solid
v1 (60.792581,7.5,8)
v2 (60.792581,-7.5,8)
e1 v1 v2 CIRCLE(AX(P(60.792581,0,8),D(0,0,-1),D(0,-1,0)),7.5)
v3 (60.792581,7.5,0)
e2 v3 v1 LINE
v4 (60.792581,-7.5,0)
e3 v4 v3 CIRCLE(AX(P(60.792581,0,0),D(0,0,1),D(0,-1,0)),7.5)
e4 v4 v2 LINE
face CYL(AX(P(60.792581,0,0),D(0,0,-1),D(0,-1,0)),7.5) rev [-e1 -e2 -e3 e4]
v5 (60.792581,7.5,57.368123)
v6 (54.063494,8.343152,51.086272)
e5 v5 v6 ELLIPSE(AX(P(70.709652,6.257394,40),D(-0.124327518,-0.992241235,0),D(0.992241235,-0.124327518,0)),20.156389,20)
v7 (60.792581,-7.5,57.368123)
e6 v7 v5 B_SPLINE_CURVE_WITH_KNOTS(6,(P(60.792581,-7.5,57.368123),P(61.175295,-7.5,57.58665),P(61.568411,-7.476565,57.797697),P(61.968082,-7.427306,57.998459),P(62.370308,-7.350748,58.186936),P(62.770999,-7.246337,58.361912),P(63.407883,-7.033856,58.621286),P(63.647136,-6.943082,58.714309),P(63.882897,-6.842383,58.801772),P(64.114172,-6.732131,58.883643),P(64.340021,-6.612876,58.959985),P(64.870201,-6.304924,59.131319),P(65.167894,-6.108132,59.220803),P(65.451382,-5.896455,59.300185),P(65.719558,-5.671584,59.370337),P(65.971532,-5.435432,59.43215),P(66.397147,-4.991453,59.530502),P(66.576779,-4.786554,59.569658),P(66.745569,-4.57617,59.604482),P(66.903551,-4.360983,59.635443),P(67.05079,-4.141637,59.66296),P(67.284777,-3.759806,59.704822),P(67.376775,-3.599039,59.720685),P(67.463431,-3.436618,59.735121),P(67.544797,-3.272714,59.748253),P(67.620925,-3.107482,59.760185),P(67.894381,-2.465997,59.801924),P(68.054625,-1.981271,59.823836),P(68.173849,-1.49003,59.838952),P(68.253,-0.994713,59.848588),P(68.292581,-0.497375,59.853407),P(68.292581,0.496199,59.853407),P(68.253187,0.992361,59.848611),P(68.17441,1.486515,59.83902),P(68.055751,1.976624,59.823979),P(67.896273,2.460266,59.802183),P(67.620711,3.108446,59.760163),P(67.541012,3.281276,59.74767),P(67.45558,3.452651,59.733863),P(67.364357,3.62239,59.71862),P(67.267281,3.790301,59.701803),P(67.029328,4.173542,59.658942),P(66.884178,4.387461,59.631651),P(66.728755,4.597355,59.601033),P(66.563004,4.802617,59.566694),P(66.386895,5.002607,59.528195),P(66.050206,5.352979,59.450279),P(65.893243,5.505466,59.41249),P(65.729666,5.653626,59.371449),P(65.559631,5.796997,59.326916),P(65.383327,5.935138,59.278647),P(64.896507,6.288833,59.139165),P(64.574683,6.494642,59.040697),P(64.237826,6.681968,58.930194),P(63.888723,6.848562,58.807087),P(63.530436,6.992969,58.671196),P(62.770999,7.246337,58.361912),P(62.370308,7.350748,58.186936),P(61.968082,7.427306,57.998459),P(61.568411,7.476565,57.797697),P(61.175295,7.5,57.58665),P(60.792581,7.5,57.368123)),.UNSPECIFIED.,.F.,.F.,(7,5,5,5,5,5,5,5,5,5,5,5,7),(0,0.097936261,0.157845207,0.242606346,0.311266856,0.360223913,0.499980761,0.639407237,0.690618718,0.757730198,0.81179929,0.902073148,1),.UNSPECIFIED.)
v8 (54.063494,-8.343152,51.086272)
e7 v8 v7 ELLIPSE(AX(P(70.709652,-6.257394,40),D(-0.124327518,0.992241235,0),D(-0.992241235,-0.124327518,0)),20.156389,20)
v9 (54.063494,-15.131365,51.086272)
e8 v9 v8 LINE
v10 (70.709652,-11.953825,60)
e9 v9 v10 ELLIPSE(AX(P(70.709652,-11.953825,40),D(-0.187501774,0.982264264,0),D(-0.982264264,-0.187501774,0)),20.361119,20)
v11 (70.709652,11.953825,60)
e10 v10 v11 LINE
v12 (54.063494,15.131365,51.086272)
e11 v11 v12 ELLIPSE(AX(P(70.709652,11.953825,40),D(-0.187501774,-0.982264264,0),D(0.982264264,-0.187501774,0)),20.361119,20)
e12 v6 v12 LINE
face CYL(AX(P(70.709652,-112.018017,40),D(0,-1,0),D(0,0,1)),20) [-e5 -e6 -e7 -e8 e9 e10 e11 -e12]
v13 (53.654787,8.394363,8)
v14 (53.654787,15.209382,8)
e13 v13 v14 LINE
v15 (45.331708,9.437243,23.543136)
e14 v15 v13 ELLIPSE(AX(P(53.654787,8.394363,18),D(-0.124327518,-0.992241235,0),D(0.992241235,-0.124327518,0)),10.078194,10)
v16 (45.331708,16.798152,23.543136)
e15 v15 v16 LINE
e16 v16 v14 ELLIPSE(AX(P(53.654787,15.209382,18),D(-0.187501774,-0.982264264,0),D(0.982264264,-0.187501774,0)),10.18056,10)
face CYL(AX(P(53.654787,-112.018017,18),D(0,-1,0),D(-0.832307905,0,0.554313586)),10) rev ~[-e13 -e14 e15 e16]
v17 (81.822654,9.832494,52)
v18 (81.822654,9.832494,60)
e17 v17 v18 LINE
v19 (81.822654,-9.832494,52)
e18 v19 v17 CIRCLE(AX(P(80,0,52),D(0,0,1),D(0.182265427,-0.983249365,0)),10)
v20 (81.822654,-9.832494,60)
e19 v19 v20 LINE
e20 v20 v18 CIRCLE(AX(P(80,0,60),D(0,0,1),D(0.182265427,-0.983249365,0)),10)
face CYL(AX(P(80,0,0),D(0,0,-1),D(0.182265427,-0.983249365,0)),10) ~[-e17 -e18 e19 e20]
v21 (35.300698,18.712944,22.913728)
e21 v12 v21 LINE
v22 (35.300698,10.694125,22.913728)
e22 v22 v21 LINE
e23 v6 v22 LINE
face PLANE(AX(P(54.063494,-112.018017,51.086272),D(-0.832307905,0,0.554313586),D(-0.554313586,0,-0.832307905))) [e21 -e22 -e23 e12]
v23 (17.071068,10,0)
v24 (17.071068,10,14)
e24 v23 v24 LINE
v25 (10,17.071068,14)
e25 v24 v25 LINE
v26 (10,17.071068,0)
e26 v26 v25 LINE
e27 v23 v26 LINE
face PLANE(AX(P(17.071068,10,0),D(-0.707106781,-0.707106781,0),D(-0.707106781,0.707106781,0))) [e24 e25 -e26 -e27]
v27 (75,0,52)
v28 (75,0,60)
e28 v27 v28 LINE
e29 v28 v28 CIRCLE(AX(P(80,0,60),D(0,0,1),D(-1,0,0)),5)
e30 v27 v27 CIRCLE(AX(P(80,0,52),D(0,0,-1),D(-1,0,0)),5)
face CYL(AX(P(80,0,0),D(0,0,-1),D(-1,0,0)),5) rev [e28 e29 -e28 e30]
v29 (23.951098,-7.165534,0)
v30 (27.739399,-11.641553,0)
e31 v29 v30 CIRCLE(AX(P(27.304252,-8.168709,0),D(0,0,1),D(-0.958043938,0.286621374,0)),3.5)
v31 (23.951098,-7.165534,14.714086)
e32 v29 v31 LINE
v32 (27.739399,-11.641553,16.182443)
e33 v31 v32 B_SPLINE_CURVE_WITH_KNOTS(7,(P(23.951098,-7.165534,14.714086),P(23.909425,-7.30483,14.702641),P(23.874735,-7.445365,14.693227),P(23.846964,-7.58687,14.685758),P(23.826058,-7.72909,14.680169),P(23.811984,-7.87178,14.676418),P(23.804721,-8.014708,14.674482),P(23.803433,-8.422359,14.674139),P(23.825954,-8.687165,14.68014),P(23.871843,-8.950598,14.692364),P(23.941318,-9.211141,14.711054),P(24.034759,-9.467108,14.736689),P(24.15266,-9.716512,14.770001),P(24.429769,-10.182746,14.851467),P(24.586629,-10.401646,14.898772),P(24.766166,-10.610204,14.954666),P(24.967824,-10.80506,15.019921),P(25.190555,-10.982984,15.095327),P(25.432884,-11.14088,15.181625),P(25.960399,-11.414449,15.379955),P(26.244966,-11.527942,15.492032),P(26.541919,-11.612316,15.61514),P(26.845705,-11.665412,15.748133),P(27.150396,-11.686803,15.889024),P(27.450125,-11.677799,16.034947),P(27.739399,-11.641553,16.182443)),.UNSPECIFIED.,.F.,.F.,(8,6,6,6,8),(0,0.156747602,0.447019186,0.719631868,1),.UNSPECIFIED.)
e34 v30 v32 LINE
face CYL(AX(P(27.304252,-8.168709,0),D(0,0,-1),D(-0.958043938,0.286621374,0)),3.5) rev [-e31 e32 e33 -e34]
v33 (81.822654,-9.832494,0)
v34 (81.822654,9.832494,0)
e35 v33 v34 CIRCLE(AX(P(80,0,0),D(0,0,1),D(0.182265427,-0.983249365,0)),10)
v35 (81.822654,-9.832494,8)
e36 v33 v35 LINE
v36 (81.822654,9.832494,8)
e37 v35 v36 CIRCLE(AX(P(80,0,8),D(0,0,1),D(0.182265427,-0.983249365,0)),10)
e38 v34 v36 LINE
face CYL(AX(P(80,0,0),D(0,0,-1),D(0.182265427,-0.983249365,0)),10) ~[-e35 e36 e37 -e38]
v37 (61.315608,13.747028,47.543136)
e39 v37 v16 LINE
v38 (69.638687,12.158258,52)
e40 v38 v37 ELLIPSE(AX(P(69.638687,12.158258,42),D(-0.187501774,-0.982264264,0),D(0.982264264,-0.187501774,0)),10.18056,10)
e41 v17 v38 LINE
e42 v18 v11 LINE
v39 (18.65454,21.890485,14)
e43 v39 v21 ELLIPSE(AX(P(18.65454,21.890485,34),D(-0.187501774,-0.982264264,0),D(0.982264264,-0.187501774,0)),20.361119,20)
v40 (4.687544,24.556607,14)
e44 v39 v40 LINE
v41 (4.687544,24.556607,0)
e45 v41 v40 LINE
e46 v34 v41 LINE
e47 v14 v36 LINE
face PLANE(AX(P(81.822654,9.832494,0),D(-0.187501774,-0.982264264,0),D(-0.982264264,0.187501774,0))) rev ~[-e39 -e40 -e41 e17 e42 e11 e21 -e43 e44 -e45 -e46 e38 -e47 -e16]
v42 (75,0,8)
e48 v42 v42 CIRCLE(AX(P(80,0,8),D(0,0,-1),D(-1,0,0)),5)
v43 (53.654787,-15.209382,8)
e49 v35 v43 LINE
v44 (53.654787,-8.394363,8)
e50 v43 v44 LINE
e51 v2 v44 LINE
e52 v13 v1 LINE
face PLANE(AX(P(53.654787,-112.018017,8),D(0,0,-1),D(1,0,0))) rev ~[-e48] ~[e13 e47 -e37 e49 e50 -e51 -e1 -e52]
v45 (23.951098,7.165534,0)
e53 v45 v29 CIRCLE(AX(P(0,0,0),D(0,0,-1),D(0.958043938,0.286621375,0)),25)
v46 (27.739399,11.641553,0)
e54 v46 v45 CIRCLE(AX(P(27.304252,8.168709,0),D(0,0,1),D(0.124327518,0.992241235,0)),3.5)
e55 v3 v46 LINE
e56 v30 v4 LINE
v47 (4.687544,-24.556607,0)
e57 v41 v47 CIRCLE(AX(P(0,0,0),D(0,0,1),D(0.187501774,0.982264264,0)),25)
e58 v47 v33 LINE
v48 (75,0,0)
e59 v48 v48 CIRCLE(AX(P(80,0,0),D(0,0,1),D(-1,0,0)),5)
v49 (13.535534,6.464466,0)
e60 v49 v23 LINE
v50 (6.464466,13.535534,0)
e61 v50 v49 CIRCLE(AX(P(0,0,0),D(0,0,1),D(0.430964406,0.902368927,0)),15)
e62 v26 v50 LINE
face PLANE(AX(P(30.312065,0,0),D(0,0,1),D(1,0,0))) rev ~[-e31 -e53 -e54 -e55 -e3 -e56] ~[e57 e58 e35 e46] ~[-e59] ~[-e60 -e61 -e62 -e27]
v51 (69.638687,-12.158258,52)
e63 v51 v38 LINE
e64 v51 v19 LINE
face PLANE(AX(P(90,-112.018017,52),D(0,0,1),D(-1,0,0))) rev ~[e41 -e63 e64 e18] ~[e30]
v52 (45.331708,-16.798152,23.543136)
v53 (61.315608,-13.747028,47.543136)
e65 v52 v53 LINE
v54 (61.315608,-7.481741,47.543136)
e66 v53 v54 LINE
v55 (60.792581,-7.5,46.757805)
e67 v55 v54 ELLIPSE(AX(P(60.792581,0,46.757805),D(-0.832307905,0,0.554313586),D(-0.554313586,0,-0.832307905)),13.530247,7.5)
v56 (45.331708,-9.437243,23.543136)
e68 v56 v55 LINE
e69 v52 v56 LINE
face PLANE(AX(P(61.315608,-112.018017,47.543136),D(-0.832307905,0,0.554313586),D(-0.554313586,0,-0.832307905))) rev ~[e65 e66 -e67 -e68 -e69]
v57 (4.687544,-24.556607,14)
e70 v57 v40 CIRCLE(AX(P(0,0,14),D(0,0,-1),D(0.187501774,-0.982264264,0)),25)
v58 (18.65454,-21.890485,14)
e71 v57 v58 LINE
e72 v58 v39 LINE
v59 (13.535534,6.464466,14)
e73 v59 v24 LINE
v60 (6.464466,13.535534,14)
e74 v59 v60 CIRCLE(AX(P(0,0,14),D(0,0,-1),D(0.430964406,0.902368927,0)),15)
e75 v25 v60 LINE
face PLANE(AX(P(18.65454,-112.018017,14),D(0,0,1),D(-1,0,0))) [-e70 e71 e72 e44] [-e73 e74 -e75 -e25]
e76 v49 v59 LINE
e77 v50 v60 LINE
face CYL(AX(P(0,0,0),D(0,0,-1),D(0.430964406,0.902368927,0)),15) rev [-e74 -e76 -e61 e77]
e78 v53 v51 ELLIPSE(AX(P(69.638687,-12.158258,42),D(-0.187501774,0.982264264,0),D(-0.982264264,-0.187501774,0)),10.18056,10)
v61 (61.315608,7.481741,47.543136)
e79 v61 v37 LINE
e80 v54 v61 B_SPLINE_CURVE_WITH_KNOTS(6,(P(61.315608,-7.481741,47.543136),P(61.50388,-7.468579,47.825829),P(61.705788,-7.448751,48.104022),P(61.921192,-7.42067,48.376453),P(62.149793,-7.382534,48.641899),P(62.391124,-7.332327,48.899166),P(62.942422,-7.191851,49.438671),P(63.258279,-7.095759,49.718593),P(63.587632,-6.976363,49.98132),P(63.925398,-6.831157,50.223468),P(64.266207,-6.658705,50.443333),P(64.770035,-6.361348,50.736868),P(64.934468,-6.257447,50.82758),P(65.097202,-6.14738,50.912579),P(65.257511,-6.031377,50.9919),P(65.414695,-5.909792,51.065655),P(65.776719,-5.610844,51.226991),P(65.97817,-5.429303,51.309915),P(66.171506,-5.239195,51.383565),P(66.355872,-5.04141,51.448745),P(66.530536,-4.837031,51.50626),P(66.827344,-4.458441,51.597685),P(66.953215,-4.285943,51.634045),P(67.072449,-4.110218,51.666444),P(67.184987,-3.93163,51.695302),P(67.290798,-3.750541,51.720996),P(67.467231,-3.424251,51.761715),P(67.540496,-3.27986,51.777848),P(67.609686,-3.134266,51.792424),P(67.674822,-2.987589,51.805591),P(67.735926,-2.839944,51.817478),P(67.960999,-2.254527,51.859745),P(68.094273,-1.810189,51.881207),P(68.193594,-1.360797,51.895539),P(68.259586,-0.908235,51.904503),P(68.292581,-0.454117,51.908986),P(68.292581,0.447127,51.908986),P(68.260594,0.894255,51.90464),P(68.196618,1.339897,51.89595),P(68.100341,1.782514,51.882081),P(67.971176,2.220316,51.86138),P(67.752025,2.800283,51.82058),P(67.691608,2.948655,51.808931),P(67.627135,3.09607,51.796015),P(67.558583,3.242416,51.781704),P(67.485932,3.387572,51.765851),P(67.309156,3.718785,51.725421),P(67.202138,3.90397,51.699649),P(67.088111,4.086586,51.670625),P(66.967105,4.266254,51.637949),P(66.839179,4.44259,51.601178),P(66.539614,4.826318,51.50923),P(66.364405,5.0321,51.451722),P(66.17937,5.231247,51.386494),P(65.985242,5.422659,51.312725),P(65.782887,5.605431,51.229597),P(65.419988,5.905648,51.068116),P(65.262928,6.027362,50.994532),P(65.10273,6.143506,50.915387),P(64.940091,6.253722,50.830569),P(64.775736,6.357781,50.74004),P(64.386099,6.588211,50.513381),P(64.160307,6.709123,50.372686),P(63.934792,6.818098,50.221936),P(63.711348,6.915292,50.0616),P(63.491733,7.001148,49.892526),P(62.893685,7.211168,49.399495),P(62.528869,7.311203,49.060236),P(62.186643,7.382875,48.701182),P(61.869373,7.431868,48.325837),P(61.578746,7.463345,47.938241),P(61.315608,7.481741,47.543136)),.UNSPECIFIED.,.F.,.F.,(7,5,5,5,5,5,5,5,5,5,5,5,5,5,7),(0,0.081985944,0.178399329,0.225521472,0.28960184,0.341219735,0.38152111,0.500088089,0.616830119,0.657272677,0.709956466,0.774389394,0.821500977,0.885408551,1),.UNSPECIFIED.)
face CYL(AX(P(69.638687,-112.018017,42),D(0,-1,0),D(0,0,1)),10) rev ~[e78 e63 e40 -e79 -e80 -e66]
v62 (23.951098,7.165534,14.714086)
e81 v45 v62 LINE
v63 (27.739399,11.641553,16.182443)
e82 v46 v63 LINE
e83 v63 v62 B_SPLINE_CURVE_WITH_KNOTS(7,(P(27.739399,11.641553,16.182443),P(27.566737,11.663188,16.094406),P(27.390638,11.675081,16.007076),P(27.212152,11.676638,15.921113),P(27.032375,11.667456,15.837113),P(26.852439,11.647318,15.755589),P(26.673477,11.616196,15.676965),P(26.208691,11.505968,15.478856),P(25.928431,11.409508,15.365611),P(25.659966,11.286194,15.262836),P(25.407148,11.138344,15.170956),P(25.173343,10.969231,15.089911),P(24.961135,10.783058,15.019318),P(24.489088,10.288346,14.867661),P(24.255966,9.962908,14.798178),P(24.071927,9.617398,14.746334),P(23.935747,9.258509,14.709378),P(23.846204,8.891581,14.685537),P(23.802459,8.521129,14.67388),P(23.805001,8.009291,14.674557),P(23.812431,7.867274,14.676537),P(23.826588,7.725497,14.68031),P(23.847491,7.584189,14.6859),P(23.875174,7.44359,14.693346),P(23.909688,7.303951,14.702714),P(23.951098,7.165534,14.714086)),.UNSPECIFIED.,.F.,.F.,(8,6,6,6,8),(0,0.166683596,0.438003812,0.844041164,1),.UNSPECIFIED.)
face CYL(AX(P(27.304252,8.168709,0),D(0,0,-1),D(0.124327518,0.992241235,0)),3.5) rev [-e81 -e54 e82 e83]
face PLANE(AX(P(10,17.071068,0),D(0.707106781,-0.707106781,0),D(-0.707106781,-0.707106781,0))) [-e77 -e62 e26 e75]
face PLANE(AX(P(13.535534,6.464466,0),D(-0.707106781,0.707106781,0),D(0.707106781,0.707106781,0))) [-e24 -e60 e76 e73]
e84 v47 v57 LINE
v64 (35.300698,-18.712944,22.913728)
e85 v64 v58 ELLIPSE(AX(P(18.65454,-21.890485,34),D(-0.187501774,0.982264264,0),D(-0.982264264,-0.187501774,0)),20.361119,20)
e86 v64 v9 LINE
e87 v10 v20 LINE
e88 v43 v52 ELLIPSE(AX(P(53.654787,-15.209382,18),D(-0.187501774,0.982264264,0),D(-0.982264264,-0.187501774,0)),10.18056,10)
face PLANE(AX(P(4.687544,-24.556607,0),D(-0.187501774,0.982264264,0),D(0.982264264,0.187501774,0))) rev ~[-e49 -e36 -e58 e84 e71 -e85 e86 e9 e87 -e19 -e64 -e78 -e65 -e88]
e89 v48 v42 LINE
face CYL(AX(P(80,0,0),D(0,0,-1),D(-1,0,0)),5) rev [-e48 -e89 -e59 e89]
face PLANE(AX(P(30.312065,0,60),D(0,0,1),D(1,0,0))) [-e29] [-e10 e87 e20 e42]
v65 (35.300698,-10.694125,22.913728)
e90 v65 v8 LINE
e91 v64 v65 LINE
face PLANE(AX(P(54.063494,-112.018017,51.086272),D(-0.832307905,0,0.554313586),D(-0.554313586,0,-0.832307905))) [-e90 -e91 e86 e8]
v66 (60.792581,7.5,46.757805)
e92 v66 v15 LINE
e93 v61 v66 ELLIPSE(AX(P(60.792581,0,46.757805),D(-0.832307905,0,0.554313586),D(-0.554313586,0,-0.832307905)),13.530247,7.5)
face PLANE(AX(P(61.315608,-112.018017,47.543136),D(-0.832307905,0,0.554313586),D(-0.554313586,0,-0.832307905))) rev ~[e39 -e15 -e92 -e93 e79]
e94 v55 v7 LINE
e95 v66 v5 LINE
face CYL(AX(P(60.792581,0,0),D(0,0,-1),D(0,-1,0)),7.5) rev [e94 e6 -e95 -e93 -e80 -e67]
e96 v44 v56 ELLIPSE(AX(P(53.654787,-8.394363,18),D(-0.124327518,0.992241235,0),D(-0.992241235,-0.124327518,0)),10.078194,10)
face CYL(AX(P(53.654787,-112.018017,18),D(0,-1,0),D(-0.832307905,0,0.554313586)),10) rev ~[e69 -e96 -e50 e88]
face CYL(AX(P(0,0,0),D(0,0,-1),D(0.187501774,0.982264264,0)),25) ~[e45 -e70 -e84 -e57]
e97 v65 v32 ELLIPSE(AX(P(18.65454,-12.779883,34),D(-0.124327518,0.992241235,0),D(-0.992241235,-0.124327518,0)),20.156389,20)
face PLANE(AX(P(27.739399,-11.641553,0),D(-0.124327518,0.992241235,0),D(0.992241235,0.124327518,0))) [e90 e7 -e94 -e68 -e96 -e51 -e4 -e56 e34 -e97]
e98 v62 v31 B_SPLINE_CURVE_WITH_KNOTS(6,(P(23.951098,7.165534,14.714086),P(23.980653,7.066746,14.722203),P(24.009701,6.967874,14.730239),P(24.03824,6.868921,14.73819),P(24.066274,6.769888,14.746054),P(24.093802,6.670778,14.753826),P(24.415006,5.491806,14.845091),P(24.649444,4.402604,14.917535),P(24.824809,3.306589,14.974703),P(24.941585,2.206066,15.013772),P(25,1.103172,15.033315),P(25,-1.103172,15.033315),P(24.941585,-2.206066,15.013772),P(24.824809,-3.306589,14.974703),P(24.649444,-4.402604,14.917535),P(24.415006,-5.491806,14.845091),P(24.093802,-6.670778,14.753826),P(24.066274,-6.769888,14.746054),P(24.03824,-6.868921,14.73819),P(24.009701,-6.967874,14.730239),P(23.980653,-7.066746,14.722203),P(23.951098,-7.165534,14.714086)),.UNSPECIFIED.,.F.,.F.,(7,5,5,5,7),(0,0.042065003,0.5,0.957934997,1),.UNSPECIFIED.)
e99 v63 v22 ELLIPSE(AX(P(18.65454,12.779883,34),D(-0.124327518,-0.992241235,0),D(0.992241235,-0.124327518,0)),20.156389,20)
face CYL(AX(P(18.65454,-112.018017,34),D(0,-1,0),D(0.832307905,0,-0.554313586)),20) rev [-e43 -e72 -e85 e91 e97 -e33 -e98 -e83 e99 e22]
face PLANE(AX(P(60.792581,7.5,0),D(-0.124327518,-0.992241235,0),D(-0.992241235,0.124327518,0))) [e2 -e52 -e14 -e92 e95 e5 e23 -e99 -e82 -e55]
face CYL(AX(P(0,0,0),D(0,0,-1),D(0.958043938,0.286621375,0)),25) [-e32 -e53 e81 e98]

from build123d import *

# Parameters (mm, degrees)
LEVER_ARM_PROFILE_SKETCH_R = 5
LEVER_ARM_BODY_DEPTH       = 60
ARM_RELIEF_CUT_DEPTH       = 112.018016556
ARM_RELIEF_CUT_DEPTH_BACK  = 112.018016556


with BuildPart() as part:
    # Lever Arm Profile Sketch → Lever Arm Body (new body)
    with BuildSketch(Plane.XY):
        with BuildLine():
            Line((81.822654266, 9.832493652), (4.687544359, 24.556606604))
            ThreePointArc((4.687544359, 24.556606604), (-25, 0), (4.687544359, -24.556606604))
            Line((4.687544359, -24.556606604), (81.822654266, -9.832493652))
            ThreePointArc((81.822654266, -9.832493652), (90, 0), (81.822654266, 9.832493652))
        make_face()
        with Locations(Location((80, 0, 0), (0, 0, 180))):
            Circle(LEVER_ARM_PROFILE_SKETCH_R, mode=Mode.SUBTRACT)
        with BuildLine():
            Line((60.79258109, 7.5), (27.739398554, 11.641553498))
            ThreePointArc((27.739398554, 11.641553498), (24.632664937, 10.429819806), (23.951098456, 7.165534365))
            ThreePointArc((23.951098456, 7.165534365), (25, 0), (23.951098456, -7.165534365))
            ThreePointArc((23.951098456, -7.165534365), (24.632664937, -10.429819806), (27.739398554, -11.641553498))
            Line((27.739398554, -11.641553498), (60.79258109, -7.5))
            ThreePointArc((60.79258109, -7.5), (68.29258109, 0), (60.79258109, 7.5))
        make_face(mode=Mode.SUBTRACT)
        with BuildLine():
            Line((10, 17.071067812), (6.464466094, 13.535533906))
            ThreePointArc((6.464466094, 13.535533906), (-10.606601718, -10.606601718), (13.535533906, 6.464466094))
            Line((13.535533906, 6.464466094), (17.071067812, 10))
            Line((17.071067812, 10), (10, 17.071067812))
        make_face(mode=Mode.SUBTRACT)
    extrude(amount=LEVER_ARM_BODY_DEPTH)

    # Relief Cut Profile Sketch → Arm Relief Cut (cut, two sides: drawn at the far end of the back side and taken through both)
    with BuildSketch(Plane(origin=(0, 0, 0), x_dir=(1, 0, 0), z_dir=(0, 1, 0)).offset(-ARM_RELIEF_CUT_DEPTH_BACK)):
        with BuildLine():
            Line((18.654539923, -14), (-25, -14))
            Line((-25, -14), (-25, -60))
            Line((-25, -60), (70.709652312, -60))
            ThreePointArc((70.709652312, -60), (61.268398012, -57.631299364), (54.063494219, -51.086271725))
            Line((54.063494219, -51.086271725), (35.300698016, -22.913728275))
            ThreePointArc((35.300698016, -22.913728275), (28.095794223, -16.368700636), (18.654539923, -14))
        make_face()
        with BuildLine():
            Line((53.654787377, -8), (90, -8))
            Line((90, -8), (90, -52))
            Line((90, -52), (69.638687081, -52))
            ThreePointArc((69.638687081, -52), (64.918059931, -50.815649682), (61.315608035, -47.543135862))
            Line((61.315608035, -47.543135862), (45.331708331, -23.543135862))
            ThreePointArc((45.331708331, -23.543135862), (44.839137696, -13.27937285), (53.654787377, -8))
        make_face()
    extrude(amount=ARM_RELIEF_CUT_DEPTH + ARM_RELIEF_CUT_DEPTH_BACK, mode=Mode.SUBTRACT)


solid = part.part
